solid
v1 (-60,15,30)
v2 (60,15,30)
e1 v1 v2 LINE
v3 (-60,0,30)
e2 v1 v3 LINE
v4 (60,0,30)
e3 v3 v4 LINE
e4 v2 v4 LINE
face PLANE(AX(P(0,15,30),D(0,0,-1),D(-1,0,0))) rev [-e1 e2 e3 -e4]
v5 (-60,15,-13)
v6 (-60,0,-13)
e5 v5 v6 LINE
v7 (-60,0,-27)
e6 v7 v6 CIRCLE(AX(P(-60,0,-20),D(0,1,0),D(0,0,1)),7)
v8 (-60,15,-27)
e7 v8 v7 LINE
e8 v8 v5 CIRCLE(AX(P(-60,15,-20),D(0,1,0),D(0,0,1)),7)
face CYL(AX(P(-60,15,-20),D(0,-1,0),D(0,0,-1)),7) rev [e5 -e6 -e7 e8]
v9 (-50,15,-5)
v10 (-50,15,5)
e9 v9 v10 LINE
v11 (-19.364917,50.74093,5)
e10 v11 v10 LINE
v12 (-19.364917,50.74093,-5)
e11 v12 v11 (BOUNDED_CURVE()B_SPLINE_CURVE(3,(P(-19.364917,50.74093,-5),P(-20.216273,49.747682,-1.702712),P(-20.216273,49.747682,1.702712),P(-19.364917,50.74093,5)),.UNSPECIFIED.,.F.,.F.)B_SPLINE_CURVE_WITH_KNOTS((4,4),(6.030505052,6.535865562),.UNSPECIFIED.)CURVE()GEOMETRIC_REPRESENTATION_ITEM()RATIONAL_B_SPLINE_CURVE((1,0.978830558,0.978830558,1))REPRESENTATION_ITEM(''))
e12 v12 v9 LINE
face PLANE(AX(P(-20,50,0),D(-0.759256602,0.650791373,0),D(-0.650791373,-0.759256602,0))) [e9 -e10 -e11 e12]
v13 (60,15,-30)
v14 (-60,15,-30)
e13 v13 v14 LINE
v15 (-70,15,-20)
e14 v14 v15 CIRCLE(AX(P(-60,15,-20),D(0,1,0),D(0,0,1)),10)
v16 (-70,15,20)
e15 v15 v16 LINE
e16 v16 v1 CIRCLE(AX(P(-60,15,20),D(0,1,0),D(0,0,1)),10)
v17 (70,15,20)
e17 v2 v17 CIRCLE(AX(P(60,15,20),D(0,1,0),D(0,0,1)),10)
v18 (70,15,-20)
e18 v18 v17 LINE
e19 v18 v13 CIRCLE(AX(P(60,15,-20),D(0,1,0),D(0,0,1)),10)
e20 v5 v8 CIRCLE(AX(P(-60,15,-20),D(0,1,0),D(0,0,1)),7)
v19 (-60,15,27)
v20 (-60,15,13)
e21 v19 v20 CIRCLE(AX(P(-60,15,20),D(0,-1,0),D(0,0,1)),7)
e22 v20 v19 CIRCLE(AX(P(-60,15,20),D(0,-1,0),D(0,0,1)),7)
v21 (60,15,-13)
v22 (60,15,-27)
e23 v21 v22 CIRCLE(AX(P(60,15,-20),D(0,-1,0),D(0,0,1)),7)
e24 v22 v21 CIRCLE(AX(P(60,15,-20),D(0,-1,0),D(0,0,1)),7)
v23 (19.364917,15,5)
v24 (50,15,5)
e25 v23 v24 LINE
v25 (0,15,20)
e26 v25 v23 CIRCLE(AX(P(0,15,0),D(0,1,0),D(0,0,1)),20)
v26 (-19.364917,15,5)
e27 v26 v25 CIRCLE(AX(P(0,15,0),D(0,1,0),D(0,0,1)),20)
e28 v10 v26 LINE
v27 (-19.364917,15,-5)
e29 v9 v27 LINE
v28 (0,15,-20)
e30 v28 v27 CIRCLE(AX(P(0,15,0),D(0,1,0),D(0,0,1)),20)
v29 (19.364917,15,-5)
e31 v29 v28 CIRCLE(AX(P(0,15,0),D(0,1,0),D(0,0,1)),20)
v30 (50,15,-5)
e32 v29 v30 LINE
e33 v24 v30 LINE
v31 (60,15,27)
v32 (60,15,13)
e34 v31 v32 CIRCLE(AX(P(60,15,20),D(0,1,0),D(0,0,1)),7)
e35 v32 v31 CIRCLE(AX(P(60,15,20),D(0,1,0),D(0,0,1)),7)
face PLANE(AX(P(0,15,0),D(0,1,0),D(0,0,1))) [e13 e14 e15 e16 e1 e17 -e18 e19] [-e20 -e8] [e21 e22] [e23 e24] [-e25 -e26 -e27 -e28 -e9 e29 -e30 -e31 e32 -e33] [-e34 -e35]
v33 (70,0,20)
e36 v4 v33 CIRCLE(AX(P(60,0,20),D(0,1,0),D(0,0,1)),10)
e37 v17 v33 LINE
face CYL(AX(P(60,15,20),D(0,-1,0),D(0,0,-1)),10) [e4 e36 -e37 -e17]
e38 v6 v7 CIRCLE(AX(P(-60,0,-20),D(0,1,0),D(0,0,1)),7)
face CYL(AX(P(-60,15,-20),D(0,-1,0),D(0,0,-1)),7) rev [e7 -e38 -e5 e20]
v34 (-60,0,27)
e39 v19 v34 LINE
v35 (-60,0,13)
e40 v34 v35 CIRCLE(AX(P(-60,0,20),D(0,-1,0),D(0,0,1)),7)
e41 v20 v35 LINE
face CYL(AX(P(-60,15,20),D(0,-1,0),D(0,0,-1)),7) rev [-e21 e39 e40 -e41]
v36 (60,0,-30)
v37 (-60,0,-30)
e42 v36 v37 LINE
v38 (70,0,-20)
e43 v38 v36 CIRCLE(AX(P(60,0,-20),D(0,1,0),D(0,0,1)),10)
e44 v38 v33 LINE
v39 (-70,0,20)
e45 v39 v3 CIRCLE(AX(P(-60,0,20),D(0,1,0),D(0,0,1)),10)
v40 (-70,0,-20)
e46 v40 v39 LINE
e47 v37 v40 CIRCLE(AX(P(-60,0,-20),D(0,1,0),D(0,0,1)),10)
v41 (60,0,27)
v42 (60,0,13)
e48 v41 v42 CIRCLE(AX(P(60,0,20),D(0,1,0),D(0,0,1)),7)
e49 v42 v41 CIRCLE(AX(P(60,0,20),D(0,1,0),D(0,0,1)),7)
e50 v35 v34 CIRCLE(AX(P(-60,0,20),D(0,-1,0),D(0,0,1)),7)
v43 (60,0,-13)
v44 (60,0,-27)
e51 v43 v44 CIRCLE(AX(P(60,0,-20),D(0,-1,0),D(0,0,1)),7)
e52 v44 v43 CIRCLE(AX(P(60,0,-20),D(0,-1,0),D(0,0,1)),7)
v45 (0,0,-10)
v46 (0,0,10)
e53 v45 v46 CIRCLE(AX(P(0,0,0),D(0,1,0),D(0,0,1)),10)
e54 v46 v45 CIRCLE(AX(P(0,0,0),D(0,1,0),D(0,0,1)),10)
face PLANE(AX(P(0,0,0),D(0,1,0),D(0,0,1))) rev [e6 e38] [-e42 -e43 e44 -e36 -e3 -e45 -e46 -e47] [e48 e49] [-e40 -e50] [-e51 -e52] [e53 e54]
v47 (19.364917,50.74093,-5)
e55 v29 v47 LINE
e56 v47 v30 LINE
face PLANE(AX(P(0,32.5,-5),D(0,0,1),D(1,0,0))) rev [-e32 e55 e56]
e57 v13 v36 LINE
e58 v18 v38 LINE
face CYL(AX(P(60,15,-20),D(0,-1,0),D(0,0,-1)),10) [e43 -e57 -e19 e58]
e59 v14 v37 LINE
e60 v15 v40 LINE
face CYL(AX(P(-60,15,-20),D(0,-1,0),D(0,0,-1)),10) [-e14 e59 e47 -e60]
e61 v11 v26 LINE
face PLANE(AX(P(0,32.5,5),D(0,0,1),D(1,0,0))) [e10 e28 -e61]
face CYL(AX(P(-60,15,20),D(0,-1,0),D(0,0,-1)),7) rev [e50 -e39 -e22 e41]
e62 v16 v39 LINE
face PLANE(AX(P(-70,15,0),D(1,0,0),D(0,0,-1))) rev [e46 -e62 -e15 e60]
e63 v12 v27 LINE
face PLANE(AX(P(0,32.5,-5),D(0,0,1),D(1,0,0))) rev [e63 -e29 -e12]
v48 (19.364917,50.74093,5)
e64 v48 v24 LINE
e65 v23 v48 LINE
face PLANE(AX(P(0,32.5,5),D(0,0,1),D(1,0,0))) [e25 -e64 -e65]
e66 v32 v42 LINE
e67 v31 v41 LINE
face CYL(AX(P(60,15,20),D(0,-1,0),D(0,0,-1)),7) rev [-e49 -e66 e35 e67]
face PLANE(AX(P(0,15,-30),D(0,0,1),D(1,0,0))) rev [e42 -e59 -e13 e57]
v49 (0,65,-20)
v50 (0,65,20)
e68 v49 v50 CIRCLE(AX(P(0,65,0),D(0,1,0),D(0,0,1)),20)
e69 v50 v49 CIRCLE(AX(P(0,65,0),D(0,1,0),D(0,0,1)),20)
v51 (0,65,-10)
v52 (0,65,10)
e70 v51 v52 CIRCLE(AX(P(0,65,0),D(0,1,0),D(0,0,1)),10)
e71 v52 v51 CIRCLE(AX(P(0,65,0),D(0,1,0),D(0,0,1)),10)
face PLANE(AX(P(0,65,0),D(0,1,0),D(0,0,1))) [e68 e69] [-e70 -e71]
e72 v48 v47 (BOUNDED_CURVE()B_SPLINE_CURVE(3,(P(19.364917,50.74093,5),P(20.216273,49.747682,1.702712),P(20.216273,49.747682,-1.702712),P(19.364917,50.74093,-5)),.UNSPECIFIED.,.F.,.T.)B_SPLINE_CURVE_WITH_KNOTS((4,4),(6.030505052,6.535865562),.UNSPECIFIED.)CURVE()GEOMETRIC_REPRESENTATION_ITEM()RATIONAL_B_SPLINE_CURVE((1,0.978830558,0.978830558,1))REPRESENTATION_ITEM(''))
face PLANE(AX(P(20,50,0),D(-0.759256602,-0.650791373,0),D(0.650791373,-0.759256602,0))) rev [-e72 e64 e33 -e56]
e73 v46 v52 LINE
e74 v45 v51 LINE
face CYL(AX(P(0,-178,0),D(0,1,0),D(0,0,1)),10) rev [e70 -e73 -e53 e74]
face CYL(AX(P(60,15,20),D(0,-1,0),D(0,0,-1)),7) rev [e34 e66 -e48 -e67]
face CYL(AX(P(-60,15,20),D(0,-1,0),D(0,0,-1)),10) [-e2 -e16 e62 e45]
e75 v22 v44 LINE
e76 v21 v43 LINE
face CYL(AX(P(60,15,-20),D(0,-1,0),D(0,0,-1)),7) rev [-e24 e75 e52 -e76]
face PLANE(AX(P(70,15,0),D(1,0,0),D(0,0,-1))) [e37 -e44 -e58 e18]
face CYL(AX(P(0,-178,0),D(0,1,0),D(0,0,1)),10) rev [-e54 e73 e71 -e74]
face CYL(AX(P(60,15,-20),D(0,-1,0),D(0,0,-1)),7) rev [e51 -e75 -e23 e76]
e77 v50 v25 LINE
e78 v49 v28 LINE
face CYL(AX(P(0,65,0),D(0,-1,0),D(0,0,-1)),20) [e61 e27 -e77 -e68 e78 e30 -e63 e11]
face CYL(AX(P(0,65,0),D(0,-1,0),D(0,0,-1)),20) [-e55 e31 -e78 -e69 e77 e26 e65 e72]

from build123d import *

# Parameters (mm, degrees)
BASE_PLATE_PROFILE_R                 = 7
BASE_PLATE_WITH_MOUNTING_HOLES_DEPTH = 15
BEARING_BOSS_PROFILE_R               = 20
BEARING_BOSS_DEPTH                   = 50
BORE_PROFILE_R                       = 10
BEARING_BORE_DEPTH                   = 243
SUPPORT_RIB_REACH                    = 102.125
SUPPORT_RIB_PROFILE_WALL_W           = 248.347566232
SUPPORT_RIB_PROFILE_WALL_H           = 10


with BuildPart() as part:
    # Base Plate Profile → Base Plate with Mounting Holes (new body)
    with BuildSketch(Plane(origin=(0, 0, 0), x_dir=(1, 0, 0), z_dir=(0, 1, 0))):
        with BuildLine():
            Line((70, 20), (70, -20))
            ThreePointArc((70, -20), (67.071067812, -27.071067812), (60, -30))
            Line((60, -30), (-60, -30))
            ThreePointArc((-60, -30), (-67.071067812, -27.071067812), (-70, -20))
            Line((-70, -20), (-70, 20))
            ThreePointArc((-70, 20), (-67.071067812, 27.071067812), (-60, 30))
            Line((-60, 30), (60, 30))
            ThreePointArc((60, 30), (67.071067812, 27.071067812), (70, 20))
        make_face()
        with Locations(Location((60, -20, 0), (0, 0, 270))):
            Circle(BASE_PLATE_PROFILE_R, mode=Mode.SUBTRACT)
        with Locations(Location((-60, 20, 0), (0, 0, 270))):
            Circle(BASE_PLATE_PROFILE_R, mode=Mode.SUBTRACT)
        with Locations(Location((60, 20, 0), (0, 0, 270))):
            Circle(BASE_PLATE_PROFILE_R, mode=Mode.SUBTRACT)
        with Locations(Location((-60, -20, 0), (0, 0, 270))):
            Circle(BASE_PLATE_PROFILE_R, mode=Mode.SUBTRACT)
    extrude(amount=BASE_PLATE_WITH_MOUNTING_HOLES_DEPTH)

    # Bearing Boss Profile → Bearing Boss (add)
    with BuildSketch(Plane(origin=(0, 15, 0), x_dir=(1, 0, 0), z_dir=(0, 1, 0))):
        with Locations(Location((0, 0, 0), (0, 0, 270))):
            Circle(BEARING_BOSS_PROFILE_R)
    extrude(amount=BEARING_BOSS_DEPTH)

    # Bore Profile → Bearing Bore (cut)
    with BuildSketch(Plane(origin=(0, 65, 0), x_dir=(1, 0, 0), z_dir=(0, 1, 0))):
        with Locations(Location((0, 0, 0), (0, 0, 270))):
            Circle(BORE_PROFILE_R)
    extrude(amount=-BEARING_BORE_DEPTH, mode=Mode.SUBTRACT)

    # Support Rib Profile wall → Support Rib (add, up to next)
    with BuildSketch(Plane(origin=(35, 32.5, 0), x_dir=(0.650791373456, -0.759256602365, 0), z_dir=(0.759256602365, 0.650791373456, 0)), mode=Mode.PRIVATE) as support_rib_sk1:
        Rectangle(SUPPORT_RIB_PROFILE_WALL_W, SUPPORT_RIB_PROFILE_WALL_H)
    support_rib_tool1 = extrude(support_rib_sk1.sketch, amount=-SUPPORT_RIB_REACH, mode=Mode.PRIVATE) - part.part
    support_rib = support_rib_tool1.solids().sort_by_distance((35, 32.5, 0))[0]
    add(support_rib)

    # Support Rib Mirror: Support Rib across plane
    add(support_rib.mirror(Plane(origin=(0, 0, 0), x_dir=(0, 0, 1), z_dir=(1, 0, 0))))


solid = part.part
